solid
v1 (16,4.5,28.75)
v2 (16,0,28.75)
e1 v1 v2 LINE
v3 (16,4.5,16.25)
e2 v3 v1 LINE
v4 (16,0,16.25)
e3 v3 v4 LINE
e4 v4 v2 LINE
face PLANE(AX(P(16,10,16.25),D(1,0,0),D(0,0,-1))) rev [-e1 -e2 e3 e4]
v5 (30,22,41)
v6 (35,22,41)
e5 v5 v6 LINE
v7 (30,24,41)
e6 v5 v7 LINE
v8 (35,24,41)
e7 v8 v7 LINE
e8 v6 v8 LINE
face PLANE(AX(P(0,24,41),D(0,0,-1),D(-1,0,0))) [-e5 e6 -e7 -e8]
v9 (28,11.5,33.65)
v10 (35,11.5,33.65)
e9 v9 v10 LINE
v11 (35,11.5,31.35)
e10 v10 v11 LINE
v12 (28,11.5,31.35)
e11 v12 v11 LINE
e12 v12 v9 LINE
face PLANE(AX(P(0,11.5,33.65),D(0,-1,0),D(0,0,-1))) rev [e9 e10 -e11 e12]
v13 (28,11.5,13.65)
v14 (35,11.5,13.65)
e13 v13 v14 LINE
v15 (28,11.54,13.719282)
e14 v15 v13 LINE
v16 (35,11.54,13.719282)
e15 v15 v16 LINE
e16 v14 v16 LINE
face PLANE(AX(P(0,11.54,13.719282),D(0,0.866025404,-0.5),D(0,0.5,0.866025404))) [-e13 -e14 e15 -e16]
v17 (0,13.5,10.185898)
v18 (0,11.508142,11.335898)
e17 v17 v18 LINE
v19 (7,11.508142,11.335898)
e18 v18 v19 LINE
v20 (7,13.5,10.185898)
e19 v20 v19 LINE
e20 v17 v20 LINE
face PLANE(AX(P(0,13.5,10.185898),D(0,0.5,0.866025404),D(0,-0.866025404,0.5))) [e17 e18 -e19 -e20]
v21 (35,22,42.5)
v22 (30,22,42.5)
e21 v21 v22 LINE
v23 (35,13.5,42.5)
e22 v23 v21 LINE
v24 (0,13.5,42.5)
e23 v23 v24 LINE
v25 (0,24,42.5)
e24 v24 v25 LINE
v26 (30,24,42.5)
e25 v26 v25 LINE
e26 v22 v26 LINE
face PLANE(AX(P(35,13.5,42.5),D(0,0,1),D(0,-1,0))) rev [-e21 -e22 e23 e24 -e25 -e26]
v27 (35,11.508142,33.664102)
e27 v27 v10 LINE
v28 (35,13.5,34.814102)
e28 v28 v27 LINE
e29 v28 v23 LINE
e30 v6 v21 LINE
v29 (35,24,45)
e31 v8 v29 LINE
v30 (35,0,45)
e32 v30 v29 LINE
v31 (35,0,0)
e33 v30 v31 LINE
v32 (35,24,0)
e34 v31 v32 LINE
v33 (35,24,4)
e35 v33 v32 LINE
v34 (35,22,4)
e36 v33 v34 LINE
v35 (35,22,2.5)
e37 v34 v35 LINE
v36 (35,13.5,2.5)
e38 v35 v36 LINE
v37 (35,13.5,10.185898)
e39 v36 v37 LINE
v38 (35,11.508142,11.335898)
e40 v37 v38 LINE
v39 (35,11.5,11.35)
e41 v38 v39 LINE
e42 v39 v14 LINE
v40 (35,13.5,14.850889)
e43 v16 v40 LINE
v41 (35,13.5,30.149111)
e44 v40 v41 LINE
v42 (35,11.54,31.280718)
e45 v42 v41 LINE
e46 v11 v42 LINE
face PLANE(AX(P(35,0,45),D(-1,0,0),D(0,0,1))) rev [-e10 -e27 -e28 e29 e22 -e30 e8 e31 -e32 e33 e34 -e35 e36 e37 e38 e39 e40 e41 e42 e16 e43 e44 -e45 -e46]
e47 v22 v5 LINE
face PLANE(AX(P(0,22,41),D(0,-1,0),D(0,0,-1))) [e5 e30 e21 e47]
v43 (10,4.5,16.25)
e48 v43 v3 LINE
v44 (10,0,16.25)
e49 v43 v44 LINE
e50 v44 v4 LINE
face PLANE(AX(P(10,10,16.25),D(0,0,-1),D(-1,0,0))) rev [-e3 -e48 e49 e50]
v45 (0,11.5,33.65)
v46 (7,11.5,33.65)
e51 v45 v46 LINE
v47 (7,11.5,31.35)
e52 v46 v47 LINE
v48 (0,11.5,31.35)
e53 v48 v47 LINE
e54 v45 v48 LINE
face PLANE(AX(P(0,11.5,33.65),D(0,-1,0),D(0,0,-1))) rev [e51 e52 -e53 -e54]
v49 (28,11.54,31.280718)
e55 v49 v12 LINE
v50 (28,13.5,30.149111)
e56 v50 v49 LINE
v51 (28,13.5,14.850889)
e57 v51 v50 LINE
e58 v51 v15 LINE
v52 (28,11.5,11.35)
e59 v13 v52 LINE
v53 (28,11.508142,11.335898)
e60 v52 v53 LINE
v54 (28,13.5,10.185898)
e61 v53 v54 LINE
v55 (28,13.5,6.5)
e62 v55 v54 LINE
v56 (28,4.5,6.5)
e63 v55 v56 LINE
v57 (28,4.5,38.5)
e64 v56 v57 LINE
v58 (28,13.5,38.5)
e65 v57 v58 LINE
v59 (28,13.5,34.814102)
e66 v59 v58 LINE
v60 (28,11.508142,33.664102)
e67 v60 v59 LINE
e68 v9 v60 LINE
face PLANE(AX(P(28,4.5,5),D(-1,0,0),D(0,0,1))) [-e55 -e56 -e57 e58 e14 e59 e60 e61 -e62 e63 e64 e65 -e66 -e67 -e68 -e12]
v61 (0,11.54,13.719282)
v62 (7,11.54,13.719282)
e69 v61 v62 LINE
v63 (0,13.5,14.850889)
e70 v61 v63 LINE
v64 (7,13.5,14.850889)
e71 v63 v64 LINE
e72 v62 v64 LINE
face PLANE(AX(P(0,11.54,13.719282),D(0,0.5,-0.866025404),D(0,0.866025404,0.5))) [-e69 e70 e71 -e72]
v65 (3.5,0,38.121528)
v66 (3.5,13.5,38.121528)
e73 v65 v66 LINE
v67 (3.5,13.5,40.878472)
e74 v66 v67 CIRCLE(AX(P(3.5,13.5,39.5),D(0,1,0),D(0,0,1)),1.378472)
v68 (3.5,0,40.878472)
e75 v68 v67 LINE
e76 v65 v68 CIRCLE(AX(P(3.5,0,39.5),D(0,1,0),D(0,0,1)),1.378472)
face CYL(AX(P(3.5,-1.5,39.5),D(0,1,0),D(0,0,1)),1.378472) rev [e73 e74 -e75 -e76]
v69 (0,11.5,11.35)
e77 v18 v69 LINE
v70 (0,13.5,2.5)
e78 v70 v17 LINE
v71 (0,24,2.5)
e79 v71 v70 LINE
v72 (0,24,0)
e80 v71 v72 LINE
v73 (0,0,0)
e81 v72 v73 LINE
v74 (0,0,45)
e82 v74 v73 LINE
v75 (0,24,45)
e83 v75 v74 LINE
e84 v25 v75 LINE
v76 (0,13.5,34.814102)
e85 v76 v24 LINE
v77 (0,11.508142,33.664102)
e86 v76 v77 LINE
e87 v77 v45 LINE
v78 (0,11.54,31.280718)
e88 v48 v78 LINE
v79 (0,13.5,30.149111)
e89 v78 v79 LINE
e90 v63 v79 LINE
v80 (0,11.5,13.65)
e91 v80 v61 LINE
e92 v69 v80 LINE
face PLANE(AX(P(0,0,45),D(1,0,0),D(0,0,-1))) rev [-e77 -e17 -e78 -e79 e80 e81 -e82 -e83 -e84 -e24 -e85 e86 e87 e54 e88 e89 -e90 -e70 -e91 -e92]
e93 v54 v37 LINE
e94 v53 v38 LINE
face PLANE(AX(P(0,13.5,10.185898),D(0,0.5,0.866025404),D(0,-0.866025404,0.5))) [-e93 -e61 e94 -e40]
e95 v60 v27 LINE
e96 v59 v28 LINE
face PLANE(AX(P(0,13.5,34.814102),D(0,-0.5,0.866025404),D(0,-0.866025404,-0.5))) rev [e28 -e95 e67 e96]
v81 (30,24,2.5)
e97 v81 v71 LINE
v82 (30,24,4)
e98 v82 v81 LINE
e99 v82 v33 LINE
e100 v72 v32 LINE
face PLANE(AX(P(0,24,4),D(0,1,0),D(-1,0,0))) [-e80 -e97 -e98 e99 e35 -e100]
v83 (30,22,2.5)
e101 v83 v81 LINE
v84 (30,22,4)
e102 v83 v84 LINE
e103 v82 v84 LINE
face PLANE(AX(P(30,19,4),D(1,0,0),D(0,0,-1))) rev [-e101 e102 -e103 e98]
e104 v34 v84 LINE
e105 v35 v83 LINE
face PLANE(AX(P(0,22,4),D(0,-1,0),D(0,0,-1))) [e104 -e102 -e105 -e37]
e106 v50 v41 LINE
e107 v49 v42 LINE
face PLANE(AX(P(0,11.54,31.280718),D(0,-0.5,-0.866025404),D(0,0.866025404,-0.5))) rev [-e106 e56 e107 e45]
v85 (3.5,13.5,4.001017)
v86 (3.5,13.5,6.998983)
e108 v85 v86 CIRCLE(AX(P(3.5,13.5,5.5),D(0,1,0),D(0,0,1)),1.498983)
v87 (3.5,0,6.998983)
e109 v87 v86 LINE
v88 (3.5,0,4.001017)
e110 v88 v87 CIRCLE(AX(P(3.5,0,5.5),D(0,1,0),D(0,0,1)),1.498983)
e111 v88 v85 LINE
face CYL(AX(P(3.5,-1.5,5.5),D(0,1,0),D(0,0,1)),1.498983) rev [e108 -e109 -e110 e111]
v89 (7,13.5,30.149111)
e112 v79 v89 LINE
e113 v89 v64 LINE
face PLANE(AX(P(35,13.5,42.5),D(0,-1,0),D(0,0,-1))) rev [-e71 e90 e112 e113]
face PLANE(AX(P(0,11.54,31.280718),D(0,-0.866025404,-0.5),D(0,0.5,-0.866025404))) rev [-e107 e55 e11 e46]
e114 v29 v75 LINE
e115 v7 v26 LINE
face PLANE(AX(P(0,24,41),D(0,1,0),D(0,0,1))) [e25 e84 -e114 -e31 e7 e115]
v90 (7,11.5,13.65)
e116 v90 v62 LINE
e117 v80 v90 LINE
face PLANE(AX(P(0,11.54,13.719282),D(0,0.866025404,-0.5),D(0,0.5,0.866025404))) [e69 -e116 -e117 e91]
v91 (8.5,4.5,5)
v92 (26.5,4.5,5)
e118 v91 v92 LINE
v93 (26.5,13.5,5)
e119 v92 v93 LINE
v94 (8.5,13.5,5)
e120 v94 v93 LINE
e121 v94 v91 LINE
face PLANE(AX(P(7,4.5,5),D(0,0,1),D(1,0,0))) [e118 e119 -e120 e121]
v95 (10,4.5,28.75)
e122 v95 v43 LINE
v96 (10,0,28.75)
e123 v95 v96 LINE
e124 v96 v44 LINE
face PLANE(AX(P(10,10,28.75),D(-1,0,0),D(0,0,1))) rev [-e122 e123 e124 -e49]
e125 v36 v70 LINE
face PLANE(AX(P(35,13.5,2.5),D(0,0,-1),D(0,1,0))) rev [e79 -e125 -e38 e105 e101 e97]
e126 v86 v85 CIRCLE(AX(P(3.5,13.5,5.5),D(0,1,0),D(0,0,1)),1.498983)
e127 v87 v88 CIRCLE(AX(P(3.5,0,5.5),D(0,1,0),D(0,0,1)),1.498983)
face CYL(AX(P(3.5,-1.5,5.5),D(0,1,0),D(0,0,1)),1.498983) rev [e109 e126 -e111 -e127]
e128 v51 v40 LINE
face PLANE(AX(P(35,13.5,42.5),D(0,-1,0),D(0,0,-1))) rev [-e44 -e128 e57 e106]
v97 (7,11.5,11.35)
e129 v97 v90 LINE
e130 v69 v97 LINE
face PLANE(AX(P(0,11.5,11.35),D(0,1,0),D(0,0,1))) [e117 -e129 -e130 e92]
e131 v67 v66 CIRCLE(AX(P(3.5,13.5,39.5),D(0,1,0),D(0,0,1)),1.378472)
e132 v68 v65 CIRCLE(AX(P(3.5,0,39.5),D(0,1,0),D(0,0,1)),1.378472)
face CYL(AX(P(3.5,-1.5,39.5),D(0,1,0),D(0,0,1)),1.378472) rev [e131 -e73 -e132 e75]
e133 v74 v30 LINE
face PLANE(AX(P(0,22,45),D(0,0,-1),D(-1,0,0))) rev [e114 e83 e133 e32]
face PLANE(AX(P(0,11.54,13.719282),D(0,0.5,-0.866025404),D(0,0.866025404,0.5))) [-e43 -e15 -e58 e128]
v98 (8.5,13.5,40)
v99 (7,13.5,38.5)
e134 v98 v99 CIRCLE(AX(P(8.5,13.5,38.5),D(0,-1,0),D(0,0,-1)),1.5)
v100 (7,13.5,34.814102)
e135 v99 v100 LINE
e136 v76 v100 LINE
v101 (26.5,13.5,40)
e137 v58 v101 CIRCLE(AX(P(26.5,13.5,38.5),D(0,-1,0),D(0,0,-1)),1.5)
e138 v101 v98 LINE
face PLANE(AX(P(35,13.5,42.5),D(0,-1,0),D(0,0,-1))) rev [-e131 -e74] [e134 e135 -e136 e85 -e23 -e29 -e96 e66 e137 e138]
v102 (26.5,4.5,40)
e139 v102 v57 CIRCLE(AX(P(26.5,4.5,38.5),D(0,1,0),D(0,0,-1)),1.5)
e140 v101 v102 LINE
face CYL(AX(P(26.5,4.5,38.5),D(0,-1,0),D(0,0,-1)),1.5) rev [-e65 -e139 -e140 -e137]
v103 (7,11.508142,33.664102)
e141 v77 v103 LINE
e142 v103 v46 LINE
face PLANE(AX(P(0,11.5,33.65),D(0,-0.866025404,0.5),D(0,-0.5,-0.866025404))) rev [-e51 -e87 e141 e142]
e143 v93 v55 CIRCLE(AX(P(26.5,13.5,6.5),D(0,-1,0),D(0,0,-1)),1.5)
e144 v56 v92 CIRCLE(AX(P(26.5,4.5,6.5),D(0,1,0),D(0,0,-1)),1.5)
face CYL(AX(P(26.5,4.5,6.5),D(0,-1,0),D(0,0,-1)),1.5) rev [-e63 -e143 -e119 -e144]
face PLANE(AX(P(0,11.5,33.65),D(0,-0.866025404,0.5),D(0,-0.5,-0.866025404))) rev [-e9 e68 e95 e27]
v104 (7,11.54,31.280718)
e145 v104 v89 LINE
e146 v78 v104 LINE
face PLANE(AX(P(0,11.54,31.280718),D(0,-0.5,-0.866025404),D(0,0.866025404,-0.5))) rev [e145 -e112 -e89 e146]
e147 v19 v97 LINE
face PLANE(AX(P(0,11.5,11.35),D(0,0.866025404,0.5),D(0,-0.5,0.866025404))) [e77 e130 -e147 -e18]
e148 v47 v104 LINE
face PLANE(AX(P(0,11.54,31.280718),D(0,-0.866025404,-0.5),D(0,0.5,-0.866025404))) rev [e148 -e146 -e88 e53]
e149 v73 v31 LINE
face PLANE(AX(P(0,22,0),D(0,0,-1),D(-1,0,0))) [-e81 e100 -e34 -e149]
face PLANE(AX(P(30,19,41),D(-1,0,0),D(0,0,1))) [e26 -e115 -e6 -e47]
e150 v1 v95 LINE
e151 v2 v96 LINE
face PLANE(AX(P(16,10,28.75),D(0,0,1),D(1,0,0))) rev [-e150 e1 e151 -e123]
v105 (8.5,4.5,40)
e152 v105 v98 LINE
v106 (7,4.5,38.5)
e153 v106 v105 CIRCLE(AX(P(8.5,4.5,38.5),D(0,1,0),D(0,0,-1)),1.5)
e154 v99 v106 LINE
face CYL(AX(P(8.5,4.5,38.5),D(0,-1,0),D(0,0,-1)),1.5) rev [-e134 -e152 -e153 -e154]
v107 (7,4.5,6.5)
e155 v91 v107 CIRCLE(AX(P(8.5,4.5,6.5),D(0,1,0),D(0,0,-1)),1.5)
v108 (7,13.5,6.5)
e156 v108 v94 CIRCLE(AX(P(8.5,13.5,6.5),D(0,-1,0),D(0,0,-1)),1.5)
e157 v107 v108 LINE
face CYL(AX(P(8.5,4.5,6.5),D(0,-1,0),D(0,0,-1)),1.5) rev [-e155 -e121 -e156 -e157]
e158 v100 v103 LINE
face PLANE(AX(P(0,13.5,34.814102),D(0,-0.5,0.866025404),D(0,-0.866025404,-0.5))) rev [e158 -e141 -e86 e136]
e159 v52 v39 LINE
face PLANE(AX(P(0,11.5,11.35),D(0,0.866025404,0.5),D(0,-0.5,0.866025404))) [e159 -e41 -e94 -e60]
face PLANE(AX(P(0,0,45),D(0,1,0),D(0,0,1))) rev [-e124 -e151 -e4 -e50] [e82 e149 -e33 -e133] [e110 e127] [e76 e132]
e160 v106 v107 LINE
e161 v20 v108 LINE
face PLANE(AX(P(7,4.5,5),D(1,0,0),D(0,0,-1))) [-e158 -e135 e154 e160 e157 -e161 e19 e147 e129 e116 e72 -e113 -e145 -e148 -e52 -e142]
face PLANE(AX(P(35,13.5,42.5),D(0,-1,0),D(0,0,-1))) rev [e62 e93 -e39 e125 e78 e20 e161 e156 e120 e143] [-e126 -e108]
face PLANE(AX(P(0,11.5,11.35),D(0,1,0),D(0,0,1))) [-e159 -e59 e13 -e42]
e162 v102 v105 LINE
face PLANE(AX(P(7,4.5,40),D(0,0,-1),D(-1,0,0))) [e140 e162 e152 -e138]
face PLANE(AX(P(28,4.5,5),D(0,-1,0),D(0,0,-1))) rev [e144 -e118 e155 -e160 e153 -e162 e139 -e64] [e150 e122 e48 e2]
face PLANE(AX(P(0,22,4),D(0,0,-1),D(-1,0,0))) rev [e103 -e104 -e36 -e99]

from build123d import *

# Parameters (mm, degrees)
SKETCH_1_W           = 35
SKETCH_1_H           = 22
EXTRUDE_1_DEPTH      = 45
SKETCH_2_W           = 35
SKETCH_2_H           = 21
CUT_EXTRUDE_1_DEPTH  = 17.5
SKETCH_3_W           = 40
SKETCH_3_H           = 8.5
CUT_EXTRUDE_2_DEPTH  = 62.10646447
FILLET_1_R           = 1.5
SKETCH_4_W           = 35
SKETCH_4_H           = 2
EXTRUDE_2_DEPTH      = 4
SKETCH_5_W           = 35
SKETCH_5_H           = 2
EXTRUDE_3_DEPTH      = 4
SKETCH_9_R           = 1.498982583
SKETCH_9_R_2         = 1.378471611
CUT_EXTRUDE_5_DEPTH  = 15
SKETCH_10_W          = 30
SKETCH_10_H          = 1.5
CUT_EXTRUDE_6_DEPTH  = 5
SKETCH_13_W          = 6
SKETCH_13_H          = 12.5
CUT_EXTRUDE_9_DEPTH  = 10
CUT_EXTRUDE_10_DEPTH = 62.854668377


with BuildPart() as part:
    # 草图1 → 拉伸1 (new body)
    with BuildSketch(Plane.XY):
        with Locations((17.5, 11)):
            Rectangle(SKETCH_1_W, SKETCH_1_H)
    extrude(amount=EXTRUDE_1_DEPTH)

    # 草图2 → 切除-拉伸1 (cut)
    with BuildSketch(Plane(origin=(20, 22, 0), x_dir=(0, 0, 1), z_dir=(0, -1, 0))):
        with Locations((22.5, 2.5)):
            Rectangle(SKETCH_2_W, SKETCH_2_H)
    extrude(amount=CUT_EXTRUDE_1_DEPTH, mode=Mode.SUBTRACT)

    # 草图3 → 切除-拉伸2 (cut, through all)
    with BuildSketch(Plane.ZY):
        with Locations((22.5, 17.75)):
            Rectangle(SKETCH_3_W, SKETCH_3_H)
    extrude(amount=-CUT_EXTRUDE_2_DEPTH, mode=Mode.SUBTRACT)

    # 圆角1
    fillet_1_edges = [part.edges().sort_by_distance(p)[0] for p in [
        (7, 9, 5),
        (28, 9, 5),
        (28, 9, 40),
        (7, 9, 40),
    ]]
    fillet(fillet_1_edges, radius=FILLET_1_R)

    # 草图4 → 拉伸2 (add)
    with BuildSketch(Plane.XY.offset(45)):
        with Locations((17.5, 23)):
            Rectangle(SKETCH_4_W, SKETCH_4_H)
    extrude(amount=-EXTRUDE_2_DEPTH)

    # 草图5 → 拉伸3 (add)
    with BuildSketch(Plane(origin=(0, 0, 0), x_dir=(-1, 0, 0), z_dir=(0, 0, -1))):
        with Locations((-17.5, 23)):
            Rectangle(SKETCH_5_W, SKETCH_5_H)
    extrude(amount=-EXTRUDE_3_DEPTH)

    # 草图9 → 切除-拉伸5 (cut)
    with BuildSketch(Plane(origin=(0, 13.5, 0), x_dir=(1, 0, 0), z_dir=(0, 1, 0))):
        with Locations(Location((3.5, -5.5, 0), (0, 0, 270))):
            Circle(SKETCH_9_R)
        with Locations(Location((3.5, -39.5, 0), (0, 0, 270))):
            Circle(SKETCH_9_R_2)
    extrude(amount=-CUT_EXTRUDE_5_DEPTH, mode=Mode.SUBTRACT)

    # 草图10 → 切除-拉伸6 (cut)
    with BuildSketch(Plane.XZ.offset(-24)):
        with Locations((15, 41.75)):
            Rectangle(SKETCH_10_W, SKETCH_10_H)
    cut_extrude_6 = extrude(amount=CUT_EXTRUDE_6_DEPTH, mode=Mode.SUBTRACT)

    # 镜向1: 切除-拉伸6 across plane
    add(cut_extrude_6.mirror(Plane(origin=(0, 0, 22.5), x_dir=(1, 0, 0), z_dir=(0, 0, -1))), mode=Mode.SUBTRACT)

    # 草图13 → 切除-拉伸9 (cut)
    with BuildSketch(Plane.XZ):
        with Locations((13, 22.5)):
            Rectangle(SKETCH_13_W, SKETCH_13_H)
    extrude(amount=-CUT_EXTRUDE_9_DEPTH, mode=Mode.SUBTRACT)

    # 草图15 → 切除-拉伸10 (cut, through all)
    with BuildSketch(Plane(origin=(35, 0, 0), x_dir=(0, 0, -1), z_dir=(1, 0, 0))):
        Polygon((-31.280717968, 11.54), (-31.35, 11.5), (-33.65, 11.5), (-33.664101615, 11.508141571), (-34.814101615, 13.5), (-30.14911144, 13.5), align=None)
    cut_extrude_10 = extrude(amount=-CUT_EXTRUDE_10_DEPTH, mode=Mode.SUBTRACT)

    # 镜向2: 切除-拉伸10 across plane
    add(cut_extrude_10.mirror(Plane(origin=(0, 0, 22.5), x_dir=(1, 0, 0), z_dir=(0, 0, -1))), mode=Mode.SUBTRACT)


solid = part.part
